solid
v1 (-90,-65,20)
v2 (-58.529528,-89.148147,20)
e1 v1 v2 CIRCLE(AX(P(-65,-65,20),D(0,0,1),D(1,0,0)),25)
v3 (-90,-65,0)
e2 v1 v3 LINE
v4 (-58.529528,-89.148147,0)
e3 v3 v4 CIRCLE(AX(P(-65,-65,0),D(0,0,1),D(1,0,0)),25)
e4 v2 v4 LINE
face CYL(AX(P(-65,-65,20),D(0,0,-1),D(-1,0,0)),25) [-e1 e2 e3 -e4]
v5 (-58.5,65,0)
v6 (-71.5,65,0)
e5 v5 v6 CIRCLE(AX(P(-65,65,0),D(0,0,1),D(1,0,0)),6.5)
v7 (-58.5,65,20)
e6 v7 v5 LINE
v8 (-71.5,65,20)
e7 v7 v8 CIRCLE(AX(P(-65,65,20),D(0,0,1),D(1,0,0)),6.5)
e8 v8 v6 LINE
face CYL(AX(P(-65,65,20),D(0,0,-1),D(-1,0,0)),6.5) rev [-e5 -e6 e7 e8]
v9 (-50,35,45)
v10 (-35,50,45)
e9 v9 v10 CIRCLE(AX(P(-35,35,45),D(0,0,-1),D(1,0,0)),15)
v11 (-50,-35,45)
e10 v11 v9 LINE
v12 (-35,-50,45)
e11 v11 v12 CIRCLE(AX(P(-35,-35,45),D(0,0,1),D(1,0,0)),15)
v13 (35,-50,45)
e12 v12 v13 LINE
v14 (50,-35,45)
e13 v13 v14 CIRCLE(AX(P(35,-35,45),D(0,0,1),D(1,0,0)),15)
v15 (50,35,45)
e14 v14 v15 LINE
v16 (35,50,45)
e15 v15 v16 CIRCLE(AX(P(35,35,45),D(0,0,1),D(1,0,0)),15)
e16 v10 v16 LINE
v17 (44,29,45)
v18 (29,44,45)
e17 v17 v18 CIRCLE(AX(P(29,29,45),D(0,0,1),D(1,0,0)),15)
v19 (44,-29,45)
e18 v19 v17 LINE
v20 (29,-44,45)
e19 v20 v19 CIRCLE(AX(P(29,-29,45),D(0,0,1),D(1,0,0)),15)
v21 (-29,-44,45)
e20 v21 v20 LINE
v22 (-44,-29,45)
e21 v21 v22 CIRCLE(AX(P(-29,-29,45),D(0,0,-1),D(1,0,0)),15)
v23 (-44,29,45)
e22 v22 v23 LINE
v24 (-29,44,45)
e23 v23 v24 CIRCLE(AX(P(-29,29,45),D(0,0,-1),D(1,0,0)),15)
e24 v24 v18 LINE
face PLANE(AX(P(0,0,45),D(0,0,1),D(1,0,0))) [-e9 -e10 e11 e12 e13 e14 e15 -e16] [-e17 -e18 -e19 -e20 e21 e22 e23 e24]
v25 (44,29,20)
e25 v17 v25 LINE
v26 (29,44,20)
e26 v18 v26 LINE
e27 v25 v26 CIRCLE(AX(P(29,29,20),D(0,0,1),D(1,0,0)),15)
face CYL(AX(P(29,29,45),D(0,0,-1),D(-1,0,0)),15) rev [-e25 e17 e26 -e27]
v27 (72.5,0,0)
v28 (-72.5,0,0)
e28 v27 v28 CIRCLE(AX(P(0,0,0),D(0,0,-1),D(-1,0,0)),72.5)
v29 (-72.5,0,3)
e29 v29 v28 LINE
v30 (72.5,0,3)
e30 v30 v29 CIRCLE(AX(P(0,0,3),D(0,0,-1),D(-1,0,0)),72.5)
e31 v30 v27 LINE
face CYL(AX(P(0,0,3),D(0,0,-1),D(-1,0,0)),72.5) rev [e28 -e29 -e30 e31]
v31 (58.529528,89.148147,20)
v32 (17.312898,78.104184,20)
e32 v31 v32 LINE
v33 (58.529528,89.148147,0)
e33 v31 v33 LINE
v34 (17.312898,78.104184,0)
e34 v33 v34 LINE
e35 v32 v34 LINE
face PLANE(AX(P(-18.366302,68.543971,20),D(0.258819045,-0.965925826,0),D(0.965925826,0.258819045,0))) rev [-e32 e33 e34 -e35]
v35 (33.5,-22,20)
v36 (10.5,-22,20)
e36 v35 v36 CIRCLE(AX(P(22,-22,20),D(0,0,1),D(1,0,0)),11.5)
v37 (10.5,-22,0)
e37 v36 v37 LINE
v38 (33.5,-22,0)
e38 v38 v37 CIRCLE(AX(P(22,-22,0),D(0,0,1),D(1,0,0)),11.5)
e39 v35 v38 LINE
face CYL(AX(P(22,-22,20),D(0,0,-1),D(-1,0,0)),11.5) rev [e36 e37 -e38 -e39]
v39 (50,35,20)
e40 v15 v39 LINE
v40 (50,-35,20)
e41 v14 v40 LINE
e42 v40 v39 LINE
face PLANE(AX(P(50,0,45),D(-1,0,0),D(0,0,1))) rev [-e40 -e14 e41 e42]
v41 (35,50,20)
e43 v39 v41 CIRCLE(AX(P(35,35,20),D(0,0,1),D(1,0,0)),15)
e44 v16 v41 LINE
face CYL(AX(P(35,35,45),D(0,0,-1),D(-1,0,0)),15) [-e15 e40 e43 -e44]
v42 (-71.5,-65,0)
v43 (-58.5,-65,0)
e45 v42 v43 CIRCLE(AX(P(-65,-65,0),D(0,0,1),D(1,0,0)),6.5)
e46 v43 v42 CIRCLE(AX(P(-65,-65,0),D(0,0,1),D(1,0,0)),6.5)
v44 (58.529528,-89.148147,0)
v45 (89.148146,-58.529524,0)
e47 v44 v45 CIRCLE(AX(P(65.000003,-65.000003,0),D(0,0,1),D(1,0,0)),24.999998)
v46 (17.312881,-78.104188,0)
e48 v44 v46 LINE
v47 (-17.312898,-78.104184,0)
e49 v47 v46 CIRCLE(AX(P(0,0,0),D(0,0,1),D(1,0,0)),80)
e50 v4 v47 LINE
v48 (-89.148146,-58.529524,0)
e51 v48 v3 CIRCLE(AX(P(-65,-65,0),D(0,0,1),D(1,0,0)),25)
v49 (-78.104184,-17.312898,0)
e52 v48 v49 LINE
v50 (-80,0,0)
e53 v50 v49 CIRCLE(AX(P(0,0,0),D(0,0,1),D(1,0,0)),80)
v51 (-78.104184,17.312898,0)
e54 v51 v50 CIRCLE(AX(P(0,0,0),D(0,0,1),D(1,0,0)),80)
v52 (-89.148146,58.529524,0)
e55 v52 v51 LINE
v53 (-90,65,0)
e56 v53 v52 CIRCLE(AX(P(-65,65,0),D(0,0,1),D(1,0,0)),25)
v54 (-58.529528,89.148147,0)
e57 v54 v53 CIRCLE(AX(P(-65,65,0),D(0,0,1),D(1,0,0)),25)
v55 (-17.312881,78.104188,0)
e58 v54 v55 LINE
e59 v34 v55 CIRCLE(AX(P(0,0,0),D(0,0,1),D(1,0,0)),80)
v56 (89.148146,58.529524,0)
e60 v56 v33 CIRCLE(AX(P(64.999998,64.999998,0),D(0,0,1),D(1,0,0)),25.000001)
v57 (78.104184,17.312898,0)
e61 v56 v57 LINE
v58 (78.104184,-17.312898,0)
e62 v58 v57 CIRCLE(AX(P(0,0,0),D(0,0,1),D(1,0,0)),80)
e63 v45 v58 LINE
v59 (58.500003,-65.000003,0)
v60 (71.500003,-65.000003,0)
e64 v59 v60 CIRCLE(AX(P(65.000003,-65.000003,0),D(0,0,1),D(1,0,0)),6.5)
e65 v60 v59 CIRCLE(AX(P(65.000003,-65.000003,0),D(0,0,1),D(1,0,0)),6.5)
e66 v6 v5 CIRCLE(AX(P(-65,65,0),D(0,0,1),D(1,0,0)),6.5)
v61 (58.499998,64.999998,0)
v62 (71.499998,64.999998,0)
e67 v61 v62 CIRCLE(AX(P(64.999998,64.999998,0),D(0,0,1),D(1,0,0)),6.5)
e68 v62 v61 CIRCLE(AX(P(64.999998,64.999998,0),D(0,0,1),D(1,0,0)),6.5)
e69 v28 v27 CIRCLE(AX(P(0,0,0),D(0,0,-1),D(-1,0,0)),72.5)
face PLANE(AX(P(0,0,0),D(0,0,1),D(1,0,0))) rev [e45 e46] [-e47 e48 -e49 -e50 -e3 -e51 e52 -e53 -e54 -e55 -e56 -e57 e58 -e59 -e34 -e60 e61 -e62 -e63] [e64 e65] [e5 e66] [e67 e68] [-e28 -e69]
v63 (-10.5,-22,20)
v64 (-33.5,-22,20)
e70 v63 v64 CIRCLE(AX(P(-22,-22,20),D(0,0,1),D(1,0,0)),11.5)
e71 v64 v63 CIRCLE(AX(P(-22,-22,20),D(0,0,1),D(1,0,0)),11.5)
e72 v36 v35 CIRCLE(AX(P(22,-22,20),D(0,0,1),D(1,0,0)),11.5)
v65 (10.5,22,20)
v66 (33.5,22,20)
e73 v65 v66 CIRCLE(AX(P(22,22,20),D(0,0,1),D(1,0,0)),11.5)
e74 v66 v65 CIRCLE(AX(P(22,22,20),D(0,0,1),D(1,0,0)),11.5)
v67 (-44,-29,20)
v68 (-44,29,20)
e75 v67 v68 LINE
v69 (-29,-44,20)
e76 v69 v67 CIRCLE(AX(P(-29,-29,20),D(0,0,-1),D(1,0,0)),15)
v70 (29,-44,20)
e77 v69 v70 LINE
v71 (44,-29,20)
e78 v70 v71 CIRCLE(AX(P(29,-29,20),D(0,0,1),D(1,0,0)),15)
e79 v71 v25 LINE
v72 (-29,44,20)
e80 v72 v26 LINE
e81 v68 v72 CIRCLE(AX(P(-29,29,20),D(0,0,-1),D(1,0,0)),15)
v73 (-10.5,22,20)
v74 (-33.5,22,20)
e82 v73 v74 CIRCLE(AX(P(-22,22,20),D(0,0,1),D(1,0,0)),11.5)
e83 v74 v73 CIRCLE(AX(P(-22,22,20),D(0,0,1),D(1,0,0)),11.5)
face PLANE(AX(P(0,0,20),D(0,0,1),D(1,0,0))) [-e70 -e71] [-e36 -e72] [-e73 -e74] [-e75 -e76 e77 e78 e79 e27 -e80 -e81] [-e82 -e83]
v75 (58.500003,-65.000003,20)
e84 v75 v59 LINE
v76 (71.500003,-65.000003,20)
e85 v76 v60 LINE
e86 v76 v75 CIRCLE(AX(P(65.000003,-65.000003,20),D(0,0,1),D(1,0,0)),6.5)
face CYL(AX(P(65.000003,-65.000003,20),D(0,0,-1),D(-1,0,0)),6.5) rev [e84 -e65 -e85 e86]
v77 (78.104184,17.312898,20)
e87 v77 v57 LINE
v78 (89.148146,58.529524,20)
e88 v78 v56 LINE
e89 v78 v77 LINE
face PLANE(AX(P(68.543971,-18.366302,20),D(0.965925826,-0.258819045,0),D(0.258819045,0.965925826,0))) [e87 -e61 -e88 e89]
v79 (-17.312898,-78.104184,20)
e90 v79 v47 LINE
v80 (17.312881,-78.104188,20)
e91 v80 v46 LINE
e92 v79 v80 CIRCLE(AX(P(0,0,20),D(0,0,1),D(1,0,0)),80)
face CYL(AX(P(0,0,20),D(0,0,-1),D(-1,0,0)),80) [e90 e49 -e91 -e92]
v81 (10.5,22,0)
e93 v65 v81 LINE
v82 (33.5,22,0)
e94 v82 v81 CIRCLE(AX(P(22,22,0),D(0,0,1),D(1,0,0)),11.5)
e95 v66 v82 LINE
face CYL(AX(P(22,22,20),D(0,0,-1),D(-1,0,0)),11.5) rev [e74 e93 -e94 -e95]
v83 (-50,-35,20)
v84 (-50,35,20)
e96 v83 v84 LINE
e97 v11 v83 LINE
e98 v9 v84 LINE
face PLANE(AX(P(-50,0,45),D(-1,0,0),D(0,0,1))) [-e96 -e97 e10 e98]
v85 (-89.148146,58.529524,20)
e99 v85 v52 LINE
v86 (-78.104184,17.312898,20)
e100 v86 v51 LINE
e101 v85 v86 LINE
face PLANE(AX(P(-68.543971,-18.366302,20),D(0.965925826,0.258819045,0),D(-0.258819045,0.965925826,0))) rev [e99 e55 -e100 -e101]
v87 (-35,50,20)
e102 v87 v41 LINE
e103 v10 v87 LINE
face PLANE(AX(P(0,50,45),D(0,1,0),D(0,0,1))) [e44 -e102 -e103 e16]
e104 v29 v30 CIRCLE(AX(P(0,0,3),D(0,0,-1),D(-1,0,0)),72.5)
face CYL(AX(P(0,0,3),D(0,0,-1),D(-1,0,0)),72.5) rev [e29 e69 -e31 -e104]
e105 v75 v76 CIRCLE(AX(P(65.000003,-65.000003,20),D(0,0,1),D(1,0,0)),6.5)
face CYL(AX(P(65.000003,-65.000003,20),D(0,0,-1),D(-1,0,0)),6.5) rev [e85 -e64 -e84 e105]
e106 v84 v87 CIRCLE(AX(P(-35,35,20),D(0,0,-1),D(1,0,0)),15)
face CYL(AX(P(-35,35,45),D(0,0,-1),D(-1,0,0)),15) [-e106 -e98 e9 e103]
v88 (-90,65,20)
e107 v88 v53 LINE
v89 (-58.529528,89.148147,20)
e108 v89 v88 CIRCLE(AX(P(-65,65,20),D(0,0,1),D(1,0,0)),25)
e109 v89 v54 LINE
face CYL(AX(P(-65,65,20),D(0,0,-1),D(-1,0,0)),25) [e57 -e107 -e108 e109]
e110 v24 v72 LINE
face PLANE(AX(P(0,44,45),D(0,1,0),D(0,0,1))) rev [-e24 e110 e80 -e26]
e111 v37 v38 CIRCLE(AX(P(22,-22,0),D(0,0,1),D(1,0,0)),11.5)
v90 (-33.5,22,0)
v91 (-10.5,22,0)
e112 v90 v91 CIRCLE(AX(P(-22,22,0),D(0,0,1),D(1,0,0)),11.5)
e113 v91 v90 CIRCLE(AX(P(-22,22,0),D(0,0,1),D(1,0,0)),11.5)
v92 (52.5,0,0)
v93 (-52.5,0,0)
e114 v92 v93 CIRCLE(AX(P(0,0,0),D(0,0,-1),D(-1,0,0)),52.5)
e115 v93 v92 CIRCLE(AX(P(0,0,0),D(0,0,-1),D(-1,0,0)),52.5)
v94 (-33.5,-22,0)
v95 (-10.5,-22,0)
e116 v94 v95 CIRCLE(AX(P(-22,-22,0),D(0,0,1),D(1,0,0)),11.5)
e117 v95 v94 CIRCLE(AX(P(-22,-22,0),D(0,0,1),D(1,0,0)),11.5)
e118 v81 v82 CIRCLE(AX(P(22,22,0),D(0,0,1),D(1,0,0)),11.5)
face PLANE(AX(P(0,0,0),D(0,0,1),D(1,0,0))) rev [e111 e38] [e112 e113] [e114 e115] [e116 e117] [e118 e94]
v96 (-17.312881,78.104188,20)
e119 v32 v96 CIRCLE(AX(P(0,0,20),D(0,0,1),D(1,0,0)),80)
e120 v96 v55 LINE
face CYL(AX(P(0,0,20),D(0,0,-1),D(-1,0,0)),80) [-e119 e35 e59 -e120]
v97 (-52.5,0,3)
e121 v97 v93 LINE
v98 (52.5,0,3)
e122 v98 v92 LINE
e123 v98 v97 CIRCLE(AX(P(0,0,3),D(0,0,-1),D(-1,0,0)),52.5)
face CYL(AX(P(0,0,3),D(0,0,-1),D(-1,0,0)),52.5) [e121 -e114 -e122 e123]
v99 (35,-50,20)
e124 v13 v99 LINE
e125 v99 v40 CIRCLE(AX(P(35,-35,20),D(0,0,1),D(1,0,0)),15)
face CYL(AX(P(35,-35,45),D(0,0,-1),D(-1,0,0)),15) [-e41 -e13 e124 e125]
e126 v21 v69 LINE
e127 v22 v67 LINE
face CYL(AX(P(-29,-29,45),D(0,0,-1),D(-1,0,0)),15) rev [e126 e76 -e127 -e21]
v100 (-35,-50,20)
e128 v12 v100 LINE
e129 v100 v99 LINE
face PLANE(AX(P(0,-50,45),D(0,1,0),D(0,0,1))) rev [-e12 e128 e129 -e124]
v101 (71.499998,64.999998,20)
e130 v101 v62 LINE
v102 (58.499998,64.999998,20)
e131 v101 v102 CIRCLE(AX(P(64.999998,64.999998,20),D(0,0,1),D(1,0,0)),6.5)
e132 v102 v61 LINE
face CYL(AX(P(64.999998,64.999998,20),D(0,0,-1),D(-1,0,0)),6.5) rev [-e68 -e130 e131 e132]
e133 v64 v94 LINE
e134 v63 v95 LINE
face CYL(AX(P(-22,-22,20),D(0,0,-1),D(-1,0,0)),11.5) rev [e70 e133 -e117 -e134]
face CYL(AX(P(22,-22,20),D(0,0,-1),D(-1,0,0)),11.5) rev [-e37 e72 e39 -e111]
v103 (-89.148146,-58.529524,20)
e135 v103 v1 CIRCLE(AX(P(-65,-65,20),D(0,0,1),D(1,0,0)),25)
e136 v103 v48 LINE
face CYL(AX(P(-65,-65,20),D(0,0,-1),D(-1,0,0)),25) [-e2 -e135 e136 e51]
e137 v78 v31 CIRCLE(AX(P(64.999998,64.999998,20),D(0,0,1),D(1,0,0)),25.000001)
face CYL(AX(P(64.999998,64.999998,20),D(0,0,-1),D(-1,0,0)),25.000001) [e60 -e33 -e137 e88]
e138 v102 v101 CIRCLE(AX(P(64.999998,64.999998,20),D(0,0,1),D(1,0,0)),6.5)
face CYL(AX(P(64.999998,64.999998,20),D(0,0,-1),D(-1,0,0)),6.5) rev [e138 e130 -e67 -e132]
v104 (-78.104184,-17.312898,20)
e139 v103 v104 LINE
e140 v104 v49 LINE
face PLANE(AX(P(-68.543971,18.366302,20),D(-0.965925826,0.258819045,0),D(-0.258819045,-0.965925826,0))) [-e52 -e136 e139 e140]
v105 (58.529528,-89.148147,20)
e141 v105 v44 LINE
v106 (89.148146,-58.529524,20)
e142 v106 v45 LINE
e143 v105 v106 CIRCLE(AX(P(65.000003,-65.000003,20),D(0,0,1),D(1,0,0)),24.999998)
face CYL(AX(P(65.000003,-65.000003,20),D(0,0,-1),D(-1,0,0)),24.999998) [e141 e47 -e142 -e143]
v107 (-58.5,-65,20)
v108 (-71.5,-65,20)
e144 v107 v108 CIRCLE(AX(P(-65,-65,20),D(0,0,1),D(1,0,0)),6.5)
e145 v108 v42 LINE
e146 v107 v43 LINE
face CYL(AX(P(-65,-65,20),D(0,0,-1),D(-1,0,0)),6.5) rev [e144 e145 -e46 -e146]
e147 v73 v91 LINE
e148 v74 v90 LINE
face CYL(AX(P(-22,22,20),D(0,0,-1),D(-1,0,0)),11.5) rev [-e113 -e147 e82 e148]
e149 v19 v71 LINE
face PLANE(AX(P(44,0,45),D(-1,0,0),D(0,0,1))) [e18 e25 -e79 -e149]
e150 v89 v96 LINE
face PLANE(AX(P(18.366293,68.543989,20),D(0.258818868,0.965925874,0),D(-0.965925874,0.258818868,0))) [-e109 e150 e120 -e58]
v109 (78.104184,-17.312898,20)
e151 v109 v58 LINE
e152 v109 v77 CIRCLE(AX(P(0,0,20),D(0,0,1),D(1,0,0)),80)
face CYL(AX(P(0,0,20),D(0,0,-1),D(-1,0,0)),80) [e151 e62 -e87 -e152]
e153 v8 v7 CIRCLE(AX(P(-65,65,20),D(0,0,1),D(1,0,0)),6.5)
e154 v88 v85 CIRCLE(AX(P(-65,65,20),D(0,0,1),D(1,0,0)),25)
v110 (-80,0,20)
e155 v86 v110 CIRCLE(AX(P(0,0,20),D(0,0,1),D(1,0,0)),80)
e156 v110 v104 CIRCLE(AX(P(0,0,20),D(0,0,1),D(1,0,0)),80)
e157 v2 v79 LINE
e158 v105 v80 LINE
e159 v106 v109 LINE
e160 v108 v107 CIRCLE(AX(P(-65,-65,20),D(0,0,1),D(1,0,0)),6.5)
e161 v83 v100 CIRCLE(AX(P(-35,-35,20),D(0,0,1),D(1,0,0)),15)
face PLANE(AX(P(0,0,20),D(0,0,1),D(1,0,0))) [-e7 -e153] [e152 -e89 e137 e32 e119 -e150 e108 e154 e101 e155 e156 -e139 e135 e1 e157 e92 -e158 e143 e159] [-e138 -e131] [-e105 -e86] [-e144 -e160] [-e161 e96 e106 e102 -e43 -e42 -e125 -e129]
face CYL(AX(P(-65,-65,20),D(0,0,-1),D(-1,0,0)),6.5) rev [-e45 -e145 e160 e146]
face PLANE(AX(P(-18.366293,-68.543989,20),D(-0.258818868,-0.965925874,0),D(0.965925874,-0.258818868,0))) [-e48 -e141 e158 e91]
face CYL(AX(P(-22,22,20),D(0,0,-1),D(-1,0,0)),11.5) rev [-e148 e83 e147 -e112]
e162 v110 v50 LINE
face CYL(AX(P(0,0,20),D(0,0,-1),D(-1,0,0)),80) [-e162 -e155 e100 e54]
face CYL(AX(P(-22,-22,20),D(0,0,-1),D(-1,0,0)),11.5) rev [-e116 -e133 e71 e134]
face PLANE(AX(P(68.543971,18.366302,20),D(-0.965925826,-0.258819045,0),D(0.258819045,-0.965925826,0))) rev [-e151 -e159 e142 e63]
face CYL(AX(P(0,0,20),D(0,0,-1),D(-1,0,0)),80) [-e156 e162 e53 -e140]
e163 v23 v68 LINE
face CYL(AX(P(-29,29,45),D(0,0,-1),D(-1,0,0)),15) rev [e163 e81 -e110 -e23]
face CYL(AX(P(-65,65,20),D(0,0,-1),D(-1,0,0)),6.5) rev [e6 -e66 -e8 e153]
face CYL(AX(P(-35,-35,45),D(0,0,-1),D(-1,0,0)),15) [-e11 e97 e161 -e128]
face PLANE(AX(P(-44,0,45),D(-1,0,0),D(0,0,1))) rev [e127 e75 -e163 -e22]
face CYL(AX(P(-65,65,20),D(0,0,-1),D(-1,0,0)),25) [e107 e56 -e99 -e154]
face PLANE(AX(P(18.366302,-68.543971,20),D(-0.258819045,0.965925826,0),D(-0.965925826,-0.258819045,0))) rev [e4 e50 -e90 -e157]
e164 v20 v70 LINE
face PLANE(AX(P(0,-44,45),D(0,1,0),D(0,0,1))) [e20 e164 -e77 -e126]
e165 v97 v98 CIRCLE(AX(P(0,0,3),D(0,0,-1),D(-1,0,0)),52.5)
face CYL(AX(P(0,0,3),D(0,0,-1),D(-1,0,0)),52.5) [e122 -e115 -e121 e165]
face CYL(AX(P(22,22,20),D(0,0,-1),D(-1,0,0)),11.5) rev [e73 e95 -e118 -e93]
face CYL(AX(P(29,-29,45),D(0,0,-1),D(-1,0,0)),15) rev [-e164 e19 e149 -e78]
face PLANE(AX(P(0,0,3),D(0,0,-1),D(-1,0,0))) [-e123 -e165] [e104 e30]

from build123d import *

# Parameters (mm, degrees)
FLANGE_PROFILE_SKETCH_R   = 6.5
FLANGE_PLATE_20MM_DEPTH   = 20
FLANGE_PROFILE_SKETCH_R_2 = 11.5
FLANGE_PLATE_20MM_2_DEPTH = 20
SQUARE_BOSS_45MM_DEPTH    = 45
BOSS_POCKET_SKETCH_R      = 72.5
BOSS_POCKET_SKETCH_R_2    = 52.5
BOSS_POCKET_CUT_DEPTH     = 3


with BuildPart() as part:
    # Flange Profile Sketch → Flange Plate 20mm (new body)
    with BuildSketch(Plane.XY):
        with BuildLine():
            Line((-89.148145657, 58.529523872), (-78.104184034, 17.312897978))
            ThreePointArc((-78.104184034, 17.312897978), (-80, 0), (-78.104184034, -17.312897978))
            Line((-78.104184034, -17.312897978), (-89.148145657, -58.529523872))
            ThreePointArc((-89.148145657, -58.529523872), (-82.677671147, -82.677667913), (-58.52952829, -89.148146841))
            Line((-58.52952829, -89.148146841), (-17.312897978, -78.104184034))
            ThreePointArc((-17.312897978, -78.104184034), (-8.453e-06, -80), (17.312881472, -78.104187693))
            Line((17.312881472, -78.104187693), (58.52952829, -89.148146841))
            ThreePointArc((58.52952829, -89.148146841), (82.677672617, -82.677669383), (89.148145657, -58.529523872))
            Line((89.148145657, -58.529523872), (78.104184034, -17.312897978))
            ThreePointArc((78.104184034, -17.312897978), (80, 0), (78.104184034, 17.312897978))
            Line((78.104184034, 17.312897978), (89.148145657, 58.529523872))
            ThreePointArc((89.148145657, 58.529523872), (82.67767031, 82.677667076), (58.52952829, 89.148146841))
            Line((58.52952829, 89.148146841), (17.312897978, 78.104184034))
            ThreePointArc((17.312897978, 78.104184034), (8.453e-06, 80), (-17.312881472, 78.104187693))
            Line((-17.312881472, 78.104187693), (-58.52952829, 89.148146841))
            ThreePointArc((-58.52952829, 89.148146841), (-82.677671147, 82.677667913), (-89.148145657, 58.529523872))
        make_face()
        with Locations((-65, -65)):
            Circle(FLANGE_PROFILE_SKETCH_R, mode=Mode.SUBTRACT)
        with Locations((65.00000294, -65.00000294)):
            Circle(FLANGE_PROFILE_SKETCH_R, mode=Mode.SUBTRACT)
        with Locations((64.999998327, 64.999998327)):
            Circle(FLANGE_PROFILE_SKETCH_R, mode=Mode.SUBTRACT)
        with Locations((-65, 65)):
            Circle(FLANGE_PROFILE_SKETCH_R, mode=Mode.SUBTRACT)
        with BuildLine():
            Line((-50, -35), (-50, 35))
            ThreePointArc((-50, 35), (-45.606601718, 45.606601718), (-35, 50))
            Line((-35, 50), (35, 50))
            ThreePointArc((35, 50), (45.606601718, 45.606601718), (50, 35))
            Line((50, 35), (50, -35))
            ThreePointArc((50, -35), (45.606601718, -45.606601718), (35, -50))
            Line((35, -50), (-35, -50))
            ThreePointArc((-35, -50), (-45.606601718, -45.606601718), (-50, -35))
        make_face(mode=Mode.SUBTRACT)
    extrude(amount=FLANGE_PLATE_20MM_DEPTH)



with BuildPart() as body_2:
    # Flange Profile Sketch → Flange Plate 20mm 2 (new body)
    with BuildSketch(Plane.XY):
        with BuildLine():
            ThreePointArc((-44, 29), (-39.606601718, 39.606601718), (-29, 44))
            Line((-29, 44), (29, 44))
            ThreePointArc((29, 44), (39.606601718, 39.606601718), (44, 29))
            Line((44, 29), (44, -29))
            ThreePointArc((44, -29), (39.606601718, -39.606601718), (29, -44))
            Line((29, -44), (-29, -44))
            ThreePointArc((-29, -44), (-39.606601718, -39.606601718), (-44, -29))
            Line((-44, -29), (-44, 29))
        make_face()
        with Locations((-22, 22)):
            Circle(FLANGE_PROFILE_SKETCH_R_2, mode=Mode.SUBTRACT)
        with Locations((22, 22)):
            Circle(FLANGE_PROFILE_SKETCH_R_2, mode=Mode.SUBTRACT)
        with Locations((22, -22)):
            Circle(FLANGE_PROFILE_SKETCH_R_2, mode=Mode.SUBTRACT)
        with Locations((-22, -22)):
            Circle(FLANGE_PROFILE_SKETCH_R_2, mode=Mode.SUBTRACT)
    extrude(amount=FLANGE_PLATE_20MM_2_DEPTH)


with BuildPart() as part_1:
    add(part.part)

    add(body_2.part)  # Square Boss 45mm merges body 2
    # Sketch2_6 → Square Boss 45mm (add)
    with BuildSketch(Plane.XY):
        with BuildLine():
            ThreePointArc((-50, 35), (-45.606601718, 45.606601718), (-35, 50))
            Line((-35, 50), (35, 50))
            ThreePointArc((35, 50), (45.606601718, 45.606601718), (50, 35))
            Line((50, 35), (50, -35))
            ThreePointArc((50, -35), (45.606601718, -45.606601718), (35, -50))
            Line((35, -50), (-35, -50))
            ThreePointArc((-35, -50), (-45.606601718, -45.606601718), (-50, -35))
            Line((-50, -35), (-50, 35))
        make_face()
        with BuildLine():
            Line((-44, -29), (-44, 29))
            ThreePointArc((-44, 29), (-39.606601718, 39.606601718), (-29, 44))
            Line((-29, 44), (29, 44))
            ThreePointArc((29, 44), (39.606601718, 39.606601718), (44, 29))
            Line((44, 29), (44, -29))
            ThreePointArc((44, -29), (39.606601718, -39.606601718), (29, -44))
            Line((29, -44), (-29, -44))
            ThreePointArc((-29, -44), (-39.606601718, -39.606601718), (-44, -29))
        make_face(mode=Mode.SUBTRACT)
    extrude(amount=SQUARE_BOSS_45MM_DEPTH)

    # Boss Pocket Sketch → Boss Pocket Cut (cut)
    with BuildSketch(Plane(origin=(0, 0, 0), x_dir=(-1, 0, 0), z_dir=(0, 0, -1))):
        Circle(BOSS_POCKET_SKETCH_R)
        Circle(BOSS_POCKET_SKETCH_R_2, mode=Mode.SUBTRACT)
    extrude(amount=-BOSS_POCKET_CUT_DEPTH, mode=Mode.SUBTRACT)


solid = part_1.part
